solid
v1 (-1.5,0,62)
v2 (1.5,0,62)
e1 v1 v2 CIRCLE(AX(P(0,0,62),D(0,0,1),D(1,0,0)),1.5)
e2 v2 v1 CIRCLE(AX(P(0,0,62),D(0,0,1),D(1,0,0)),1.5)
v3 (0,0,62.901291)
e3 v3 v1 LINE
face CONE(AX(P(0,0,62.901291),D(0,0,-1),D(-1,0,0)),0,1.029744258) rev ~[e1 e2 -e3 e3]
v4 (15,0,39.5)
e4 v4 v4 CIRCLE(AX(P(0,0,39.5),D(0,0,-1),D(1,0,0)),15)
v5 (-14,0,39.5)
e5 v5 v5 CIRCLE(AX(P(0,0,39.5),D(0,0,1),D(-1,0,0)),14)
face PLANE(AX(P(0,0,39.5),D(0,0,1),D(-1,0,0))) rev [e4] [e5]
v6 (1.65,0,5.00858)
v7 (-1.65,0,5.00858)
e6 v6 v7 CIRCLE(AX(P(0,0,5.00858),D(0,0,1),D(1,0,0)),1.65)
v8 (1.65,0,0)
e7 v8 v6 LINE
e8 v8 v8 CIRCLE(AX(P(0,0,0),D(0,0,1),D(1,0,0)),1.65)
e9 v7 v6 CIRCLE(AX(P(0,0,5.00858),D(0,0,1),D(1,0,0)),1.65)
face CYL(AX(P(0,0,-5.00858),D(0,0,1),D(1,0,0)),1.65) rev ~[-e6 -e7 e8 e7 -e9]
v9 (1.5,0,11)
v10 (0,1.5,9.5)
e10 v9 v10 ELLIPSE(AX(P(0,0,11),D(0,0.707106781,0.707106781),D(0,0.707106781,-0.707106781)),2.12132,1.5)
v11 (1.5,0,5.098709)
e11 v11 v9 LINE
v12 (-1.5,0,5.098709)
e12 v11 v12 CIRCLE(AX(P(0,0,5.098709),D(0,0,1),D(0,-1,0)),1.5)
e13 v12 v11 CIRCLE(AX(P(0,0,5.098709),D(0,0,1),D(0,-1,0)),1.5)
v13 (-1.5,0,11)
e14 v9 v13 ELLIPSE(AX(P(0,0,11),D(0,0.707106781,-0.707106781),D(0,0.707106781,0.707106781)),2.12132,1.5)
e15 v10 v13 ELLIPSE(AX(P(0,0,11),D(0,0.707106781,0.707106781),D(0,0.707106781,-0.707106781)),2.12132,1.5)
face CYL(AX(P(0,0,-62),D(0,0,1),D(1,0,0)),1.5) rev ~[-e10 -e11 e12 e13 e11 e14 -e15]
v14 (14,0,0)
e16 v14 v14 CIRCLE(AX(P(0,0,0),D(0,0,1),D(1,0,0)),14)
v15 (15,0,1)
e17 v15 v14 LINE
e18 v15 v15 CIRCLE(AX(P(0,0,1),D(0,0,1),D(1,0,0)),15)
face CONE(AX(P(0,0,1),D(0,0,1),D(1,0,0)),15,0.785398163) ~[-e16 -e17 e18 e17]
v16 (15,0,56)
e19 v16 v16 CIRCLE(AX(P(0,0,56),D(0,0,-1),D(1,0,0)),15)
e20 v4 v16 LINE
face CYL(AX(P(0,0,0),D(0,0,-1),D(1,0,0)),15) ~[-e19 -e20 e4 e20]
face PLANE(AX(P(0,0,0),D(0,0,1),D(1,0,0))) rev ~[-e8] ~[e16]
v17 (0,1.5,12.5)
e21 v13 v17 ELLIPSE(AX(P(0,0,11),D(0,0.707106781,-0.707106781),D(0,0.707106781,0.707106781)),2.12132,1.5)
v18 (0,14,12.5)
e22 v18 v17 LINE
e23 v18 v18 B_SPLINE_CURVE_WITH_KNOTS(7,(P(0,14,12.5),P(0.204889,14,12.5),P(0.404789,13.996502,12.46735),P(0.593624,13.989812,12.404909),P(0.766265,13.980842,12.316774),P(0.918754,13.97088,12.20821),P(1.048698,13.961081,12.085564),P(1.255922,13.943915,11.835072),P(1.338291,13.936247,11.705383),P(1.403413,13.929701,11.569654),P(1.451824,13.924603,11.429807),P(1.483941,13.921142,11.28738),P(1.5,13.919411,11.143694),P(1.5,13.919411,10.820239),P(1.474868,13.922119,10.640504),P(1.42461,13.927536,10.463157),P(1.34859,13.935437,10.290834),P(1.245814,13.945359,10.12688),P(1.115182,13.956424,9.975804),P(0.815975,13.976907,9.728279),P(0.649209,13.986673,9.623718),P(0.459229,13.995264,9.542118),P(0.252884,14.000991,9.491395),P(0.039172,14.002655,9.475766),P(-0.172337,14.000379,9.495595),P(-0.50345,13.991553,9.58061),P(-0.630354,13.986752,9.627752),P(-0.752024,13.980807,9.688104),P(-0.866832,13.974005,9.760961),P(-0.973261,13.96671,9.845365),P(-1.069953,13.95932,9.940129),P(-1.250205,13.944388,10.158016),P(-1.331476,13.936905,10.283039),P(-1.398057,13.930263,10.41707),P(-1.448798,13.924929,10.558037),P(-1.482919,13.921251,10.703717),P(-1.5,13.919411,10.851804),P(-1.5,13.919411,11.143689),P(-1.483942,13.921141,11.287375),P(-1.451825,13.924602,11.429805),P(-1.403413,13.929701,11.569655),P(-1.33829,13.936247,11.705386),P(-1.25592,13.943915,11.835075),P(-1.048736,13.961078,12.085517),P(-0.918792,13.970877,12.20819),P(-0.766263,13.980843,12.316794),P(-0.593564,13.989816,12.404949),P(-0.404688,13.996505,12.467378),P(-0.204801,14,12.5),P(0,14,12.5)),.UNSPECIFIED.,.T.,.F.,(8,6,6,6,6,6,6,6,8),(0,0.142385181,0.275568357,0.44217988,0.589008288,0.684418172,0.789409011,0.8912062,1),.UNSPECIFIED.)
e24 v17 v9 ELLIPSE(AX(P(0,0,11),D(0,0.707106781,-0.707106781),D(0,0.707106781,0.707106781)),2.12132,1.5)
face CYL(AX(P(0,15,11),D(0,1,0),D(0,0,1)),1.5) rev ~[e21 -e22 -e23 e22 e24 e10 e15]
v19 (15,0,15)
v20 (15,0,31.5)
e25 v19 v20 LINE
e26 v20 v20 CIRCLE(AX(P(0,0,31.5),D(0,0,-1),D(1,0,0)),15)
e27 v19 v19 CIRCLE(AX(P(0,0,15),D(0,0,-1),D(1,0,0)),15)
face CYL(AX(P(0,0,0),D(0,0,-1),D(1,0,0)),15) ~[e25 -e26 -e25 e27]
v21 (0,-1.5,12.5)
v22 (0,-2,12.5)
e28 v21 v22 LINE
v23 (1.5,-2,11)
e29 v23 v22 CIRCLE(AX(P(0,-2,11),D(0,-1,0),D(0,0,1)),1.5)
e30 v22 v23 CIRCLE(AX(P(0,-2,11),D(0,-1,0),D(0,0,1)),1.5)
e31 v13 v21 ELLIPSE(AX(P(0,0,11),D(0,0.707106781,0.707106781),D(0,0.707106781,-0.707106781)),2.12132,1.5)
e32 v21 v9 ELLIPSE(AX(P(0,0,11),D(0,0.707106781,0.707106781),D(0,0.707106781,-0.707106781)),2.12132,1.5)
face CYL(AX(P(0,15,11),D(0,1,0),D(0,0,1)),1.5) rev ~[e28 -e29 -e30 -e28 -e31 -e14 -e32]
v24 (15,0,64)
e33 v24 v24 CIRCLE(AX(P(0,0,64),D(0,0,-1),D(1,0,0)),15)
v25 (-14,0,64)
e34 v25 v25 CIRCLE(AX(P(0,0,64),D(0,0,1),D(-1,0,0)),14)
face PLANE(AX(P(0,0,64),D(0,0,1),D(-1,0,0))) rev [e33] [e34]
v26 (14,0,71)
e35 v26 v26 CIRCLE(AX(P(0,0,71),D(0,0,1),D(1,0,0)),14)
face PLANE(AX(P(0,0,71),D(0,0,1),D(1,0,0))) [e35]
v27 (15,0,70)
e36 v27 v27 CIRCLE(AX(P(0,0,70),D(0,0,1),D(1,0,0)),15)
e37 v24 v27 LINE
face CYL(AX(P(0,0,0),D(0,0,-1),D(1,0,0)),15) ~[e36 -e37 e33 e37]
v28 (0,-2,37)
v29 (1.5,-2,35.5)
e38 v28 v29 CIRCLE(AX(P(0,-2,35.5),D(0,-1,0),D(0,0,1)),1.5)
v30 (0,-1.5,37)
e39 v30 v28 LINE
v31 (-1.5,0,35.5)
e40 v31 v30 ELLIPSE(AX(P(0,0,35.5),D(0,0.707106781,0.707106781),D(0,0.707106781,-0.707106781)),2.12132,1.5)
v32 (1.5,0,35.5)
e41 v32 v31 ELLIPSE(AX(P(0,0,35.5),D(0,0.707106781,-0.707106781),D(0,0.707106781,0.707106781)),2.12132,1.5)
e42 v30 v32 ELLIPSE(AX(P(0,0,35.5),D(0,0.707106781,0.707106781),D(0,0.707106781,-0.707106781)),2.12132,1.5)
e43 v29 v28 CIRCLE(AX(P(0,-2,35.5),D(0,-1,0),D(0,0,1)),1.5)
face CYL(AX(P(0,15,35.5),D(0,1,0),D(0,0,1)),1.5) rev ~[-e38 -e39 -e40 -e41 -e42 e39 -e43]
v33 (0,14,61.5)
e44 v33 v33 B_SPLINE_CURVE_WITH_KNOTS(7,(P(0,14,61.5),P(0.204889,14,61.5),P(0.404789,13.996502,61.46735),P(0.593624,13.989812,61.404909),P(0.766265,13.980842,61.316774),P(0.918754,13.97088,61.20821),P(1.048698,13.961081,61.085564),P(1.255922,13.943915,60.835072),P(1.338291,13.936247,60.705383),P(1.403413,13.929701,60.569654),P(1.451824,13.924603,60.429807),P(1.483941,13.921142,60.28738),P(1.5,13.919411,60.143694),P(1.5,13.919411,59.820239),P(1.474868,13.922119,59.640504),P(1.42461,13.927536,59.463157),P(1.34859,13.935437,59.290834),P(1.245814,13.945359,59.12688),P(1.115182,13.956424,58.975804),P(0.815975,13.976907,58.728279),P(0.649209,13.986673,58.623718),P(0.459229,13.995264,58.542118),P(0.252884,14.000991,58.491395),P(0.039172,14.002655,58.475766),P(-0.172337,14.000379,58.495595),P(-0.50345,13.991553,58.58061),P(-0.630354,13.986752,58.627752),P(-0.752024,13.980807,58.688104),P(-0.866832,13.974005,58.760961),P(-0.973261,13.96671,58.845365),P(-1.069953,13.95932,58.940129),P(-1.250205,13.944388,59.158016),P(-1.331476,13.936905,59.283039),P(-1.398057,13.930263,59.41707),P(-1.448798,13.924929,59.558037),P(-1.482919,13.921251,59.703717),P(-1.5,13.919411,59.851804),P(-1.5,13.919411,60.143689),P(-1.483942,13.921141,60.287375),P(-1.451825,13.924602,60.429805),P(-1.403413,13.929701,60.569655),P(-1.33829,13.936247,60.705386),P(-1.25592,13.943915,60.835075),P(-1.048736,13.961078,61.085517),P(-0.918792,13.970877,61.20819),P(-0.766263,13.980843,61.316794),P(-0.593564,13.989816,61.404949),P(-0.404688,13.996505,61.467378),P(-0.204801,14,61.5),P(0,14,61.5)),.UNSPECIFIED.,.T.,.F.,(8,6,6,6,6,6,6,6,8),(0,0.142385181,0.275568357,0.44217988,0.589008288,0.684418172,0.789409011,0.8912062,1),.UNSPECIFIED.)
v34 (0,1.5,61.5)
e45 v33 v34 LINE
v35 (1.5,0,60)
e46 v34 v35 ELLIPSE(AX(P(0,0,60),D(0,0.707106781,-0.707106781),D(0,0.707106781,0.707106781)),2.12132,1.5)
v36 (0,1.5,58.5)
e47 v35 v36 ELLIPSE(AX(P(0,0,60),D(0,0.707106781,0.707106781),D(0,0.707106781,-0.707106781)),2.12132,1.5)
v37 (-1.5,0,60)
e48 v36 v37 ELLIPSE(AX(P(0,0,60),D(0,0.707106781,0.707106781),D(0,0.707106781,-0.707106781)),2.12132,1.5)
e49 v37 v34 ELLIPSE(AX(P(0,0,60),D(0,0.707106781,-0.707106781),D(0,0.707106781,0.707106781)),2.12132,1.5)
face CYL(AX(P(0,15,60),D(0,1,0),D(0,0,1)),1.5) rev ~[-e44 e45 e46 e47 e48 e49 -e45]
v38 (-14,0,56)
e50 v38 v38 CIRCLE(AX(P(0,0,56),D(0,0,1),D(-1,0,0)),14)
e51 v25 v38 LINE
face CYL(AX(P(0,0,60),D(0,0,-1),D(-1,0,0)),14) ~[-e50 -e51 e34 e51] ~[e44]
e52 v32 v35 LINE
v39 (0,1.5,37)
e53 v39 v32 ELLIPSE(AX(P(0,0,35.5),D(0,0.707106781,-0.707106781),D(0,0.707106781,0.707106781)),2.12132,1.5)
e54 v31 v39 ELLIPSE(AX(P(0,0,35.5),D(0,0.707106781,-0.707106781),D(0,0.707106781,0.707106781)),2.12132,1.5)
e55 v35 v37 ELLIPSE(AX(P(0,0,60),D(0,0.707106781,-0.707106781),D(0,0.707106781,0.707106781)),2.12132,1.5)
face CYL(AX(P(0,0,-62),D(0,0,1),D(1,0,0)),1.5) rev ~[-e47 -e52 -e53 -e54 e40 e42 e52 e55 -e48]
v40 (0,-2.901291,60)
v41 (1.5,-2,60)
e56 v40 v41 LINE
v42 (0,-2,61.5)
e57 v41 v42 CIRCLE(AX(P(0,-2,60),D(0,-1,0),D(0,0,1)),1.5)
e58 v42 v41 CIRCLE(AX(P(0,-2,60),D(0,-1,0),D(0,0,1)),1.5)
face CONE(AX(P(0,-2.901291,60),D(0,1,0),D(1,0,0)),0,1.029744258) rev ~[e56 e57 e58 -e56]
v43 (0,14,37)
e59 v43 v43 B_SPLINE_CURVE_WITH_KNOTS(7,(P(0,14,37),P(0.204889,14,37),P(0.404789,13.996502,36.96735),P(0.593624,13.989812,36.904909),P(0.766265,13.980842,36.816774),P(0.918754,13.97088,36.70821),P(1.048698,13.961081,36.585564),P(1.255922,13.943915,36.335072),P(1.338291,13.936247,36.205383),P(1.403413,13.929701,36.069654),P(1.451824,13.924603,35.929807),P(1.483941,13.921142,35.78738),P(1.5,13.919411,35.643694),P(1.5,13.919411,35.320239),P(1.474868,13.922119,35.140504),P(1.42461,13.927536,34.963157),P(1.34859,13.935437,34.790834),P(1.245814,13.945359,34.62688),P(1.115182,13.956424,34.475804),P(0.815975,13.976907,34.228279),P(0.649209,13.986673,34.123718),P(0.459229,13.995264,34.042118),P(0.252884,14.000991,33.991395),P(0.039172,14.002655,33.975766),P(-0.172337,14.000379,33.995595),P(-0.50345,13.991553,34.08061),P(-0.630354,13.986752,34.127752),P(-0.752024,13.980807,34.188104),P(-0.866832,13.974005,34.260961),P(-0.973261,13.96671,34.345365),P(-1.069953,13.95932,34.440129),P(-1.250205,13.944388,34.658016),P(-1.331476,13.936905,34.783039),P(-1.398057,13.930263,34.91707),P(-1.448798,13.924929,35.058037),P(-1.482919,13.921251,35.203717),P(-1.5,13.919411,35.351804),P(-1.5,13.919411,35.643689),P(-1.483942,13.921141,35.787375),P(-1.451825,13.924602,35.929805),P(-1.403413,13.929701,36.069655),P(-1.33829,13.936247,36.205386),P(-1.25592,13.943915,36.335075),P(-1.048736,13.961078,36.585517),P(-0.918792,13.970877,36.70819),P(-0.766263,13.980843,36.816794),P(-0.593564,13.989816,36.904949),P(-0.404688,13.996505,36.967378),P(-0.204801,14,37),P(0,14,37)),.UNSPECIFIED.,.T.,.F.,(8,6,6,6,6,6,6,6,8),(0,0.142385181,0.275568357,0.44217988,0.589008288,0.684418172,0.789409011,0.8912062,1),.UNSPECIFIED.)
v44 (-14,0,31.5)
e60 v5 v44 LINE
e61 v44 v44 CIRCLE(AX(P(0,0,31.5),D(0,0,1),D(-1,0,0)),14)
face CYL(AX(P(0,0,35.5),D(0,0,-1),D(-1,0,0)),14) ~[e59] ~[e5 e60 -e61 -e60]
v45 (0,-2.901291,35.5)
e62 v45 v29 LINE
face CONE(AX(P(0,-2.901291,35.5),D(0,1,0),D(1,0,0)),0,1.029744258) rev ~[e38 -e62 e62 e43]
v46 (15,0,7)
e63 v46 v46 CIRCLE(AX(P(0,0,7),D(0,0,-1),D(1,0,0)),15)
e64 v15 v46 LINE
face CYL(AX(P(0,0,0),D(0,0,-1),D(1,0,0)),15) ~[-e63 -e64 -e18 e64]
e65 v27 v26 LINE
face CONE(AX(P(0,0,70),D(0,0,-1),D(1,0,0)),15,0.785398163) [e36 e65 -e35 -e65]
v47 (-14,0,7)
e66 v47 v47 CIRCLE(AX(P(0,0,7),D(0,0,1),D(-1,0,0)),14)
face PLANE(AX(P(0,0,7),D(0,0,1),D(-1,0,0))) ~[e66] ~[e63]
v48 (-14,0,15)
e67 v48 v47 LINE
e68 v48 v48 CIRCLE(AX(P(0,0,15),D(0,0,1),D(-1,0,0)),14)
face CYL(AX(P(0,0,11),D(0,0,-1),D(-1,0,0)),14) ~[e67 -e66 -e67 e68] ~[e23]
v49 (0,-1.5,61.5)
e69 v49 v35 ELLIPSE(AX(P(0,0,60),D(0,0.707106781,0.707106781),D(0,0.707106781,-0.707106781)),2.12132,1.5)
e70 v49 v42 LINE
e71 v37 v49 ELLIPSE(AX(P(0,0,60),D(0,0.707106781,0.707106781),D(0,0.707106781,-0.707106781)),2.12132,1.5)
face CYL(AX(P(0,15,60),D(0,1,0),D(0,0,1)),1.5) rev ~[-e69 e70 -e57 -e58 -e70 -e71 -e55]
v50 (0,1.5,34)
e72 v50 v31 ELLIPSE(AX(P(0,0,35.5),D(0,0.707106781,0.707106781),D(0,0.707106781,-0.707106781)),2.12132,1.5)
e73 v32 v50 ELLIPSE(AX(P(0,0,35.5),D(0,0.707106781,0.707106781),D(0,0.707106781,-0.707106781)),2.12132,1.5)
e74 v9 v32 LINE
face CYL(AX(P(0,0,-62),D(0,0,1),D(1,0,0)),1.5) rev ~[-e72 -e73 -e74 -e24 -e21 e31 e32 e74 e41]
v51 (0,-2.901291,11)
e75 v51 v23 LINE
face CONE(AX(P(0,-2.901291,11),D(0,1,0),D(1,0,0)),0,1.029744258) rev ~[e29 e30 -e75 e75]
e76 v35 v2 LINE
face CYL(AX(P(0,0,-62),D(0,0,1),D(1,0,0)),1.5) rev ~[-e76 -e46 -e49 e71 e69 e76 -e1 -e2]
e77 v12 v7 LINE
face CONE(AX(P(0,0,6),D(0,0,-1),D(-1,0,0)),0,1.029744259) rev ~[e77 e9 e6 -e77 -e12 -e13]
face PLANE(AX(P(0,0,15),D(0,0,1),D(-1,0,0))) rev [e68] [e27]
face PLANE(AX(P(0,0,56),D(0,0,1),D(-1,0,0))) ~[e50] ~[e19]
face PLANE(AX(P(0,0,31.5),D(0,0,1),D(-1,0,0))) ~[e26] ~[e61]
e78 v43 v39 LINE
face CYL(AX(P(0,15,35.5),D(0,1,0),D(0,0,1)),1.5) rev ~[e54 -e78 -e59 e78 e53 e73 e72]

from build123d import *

# Parameters (mm, degrees)
SKETCH1_R                  = 15
BOSS_EXTRUDE1_DEPTH        = 71
CHAMFER1_SIZE              = 1
SKETCH6_R                  = 1.5
CUT_EXTRUDE1_DEPTH         = 17
SIZE_MM_DOWEL_HOLE_6_D     = 3
SIZE_MM_DOWEL_HOLE_6_DEPTH = 17
SIZE_MM_DOWEL_HOLE_6_TIP   = 0.901290929
SKETCH17_W                 = 2
SKETCH17_H                 = 8
SIZE_MM_DOWEL_HOLE_7_D     = 3
SIZE_MM_DOWEL_HOLE_7_DEPTH = 62
SIZE_MM_DOWEL_HOLE_7_TIP   = 0.901290929
M4_TAPPED_HOLE1_D          = 3.3
M4_TAPPED_HOLE1_DEPTH      = 5.008579979
M4_TAPPED_HOLE1_TIP        = 0.991420021


with BuildPart() as part:
    # Sketch1 → Boss-Extrude1 (new body)
    with BuildSketch(Plane.XY):
        Circle(SKETCH1_R)
    extrude(amount=BOSS_EXTRUDE1_DEPTH)

    # Chamfer1
    chamfer1_edges = [part.edges().sort_by_distance(p)[0] for p in [
        (-15, 0, 0),
        (-15, 0, 71),
    ]]
    chamfer(chamfer1_edges, length=CHAMFER1_SIZE)

    # Sketch6 → Cut-Extrude1 (cut)
    with BuildSketch(Plane(origin=(0, 15, 0), x_dir=(1, 0, 0), z_dir=(0, 1, 0))):
        with Locations(Location((0, -11, 0), (0, 0, 270))):
            Circle(SKETCH6_R)
        with Locations(Location((0, -35.5, 0), (0, 0, 270))):
            Circle(SKETCH6_R)
        with Locations(Location((0, -60, 0), (0, 0, 270))):
            Circle(SKETCH6_R)
    extrude(amount=-CUT_EXTRUDE1_DEPTH, mode=Mode.SUBTRACT)

    # Size mm dowel hole 6
    with Locations(Plane(origin=(0, 15, 0), x_dir=(1, 0, 0), z_dir=(0, 1, 0))):
        with Locations((0, -11), (0, -35.5), (0, -60)):
            Hole(SIZE_MM_DOWEL_HOLE_6_D / 2, depth=SIZE_MM_DOWEL_HOLE_6_DEPTH)
            with Locations((0, 0, -(SIZE_MM_DOWEL_HOLE_6_DEPTH + SIZE_MM_DOWEL_HOLE_6_TIP / 2))):  # 118° drill point
                Cone(0, SIZE_MM_DOWEL_HOLE_6_D / 2, SIZE_MM_DOWEL_HOLE_6_TIP, mode=Mode.SUBTRACT)

    # Sketch17 → Cut-Revolve1 (revolve, cut)
    with BuildSketch(Plane(origin=(0, 0, 0), x_dir=(1, 0, 0), z_dir=(0, 1, 0)), mode=Mode.PRIVATE) as cut_revolve1_sk:
        with Locations((15, -11)):
            Rectangle(SKETCH17_W, SKETCH17_H)
        with Locations((15, -35.5)):
            Rectangle(SKETCH17_W, SKETCH17_H)
        with Locations((15, -60)):
            Rectangle(SKETCH17_W, SKETCH17_H)
    revolve(cut_revolve1_sk.sketch.rotate(Axis((0, 0, 0), (0, 0, 1)), 180), axis=Axis((0, 0, 0), (0, 0, 1)), mode=Mode.SUBTRACT)

    # Size mm dowel hole 7
    with Locations(Plane(origin=(0, 0, 0), x_dir=(-1, 0, 0), z_dir=(0, 0, -1))):
        with Locations((0, 0)):
            Hole(SIZE_MM_DOWEL_HOLE_7_D / 2, depth=SIZE_MM_DOWEL_HOLE_7_DEPTH)
            with Locations((0, 0, -(SIZE_MM_DOWEL_HOLE_7_DEPTH + SIZE_MM_DOWEL_HOLE_7_TIP / 2))):  # 118° drill point
                Cone(0, SIZE_MM_DOWEL_HOLE_7_D / 2, SIZE_MM_DOWEL_HOLE_7_TIP, mode=Mode.SUBTRACT)

    # M4 Tapped Hole1
    with Locations(Plane(origin=(0, 0, 0), x_dir=(-1, 0, 0), z_dir=(0, 0, -1))):
        with Locations((0, 0)):
            Hole(M4_TAPPED_HOLE1_D / 2, depth=M4_TAPPED_HOLE1_DEPTH)
            with Locations((0, 0, -(M4_TAPPED_HOLE1_DEPTH + M4_TAPPED_HOLE1_TIP / 2))):  # 118° drill point
                Cone(0, M4_TAPPED_HOLE1_D / 2, M4_TAPPED_HOLE1_TIP, mode=Mode.SUBTRACT)


solid = part.part
